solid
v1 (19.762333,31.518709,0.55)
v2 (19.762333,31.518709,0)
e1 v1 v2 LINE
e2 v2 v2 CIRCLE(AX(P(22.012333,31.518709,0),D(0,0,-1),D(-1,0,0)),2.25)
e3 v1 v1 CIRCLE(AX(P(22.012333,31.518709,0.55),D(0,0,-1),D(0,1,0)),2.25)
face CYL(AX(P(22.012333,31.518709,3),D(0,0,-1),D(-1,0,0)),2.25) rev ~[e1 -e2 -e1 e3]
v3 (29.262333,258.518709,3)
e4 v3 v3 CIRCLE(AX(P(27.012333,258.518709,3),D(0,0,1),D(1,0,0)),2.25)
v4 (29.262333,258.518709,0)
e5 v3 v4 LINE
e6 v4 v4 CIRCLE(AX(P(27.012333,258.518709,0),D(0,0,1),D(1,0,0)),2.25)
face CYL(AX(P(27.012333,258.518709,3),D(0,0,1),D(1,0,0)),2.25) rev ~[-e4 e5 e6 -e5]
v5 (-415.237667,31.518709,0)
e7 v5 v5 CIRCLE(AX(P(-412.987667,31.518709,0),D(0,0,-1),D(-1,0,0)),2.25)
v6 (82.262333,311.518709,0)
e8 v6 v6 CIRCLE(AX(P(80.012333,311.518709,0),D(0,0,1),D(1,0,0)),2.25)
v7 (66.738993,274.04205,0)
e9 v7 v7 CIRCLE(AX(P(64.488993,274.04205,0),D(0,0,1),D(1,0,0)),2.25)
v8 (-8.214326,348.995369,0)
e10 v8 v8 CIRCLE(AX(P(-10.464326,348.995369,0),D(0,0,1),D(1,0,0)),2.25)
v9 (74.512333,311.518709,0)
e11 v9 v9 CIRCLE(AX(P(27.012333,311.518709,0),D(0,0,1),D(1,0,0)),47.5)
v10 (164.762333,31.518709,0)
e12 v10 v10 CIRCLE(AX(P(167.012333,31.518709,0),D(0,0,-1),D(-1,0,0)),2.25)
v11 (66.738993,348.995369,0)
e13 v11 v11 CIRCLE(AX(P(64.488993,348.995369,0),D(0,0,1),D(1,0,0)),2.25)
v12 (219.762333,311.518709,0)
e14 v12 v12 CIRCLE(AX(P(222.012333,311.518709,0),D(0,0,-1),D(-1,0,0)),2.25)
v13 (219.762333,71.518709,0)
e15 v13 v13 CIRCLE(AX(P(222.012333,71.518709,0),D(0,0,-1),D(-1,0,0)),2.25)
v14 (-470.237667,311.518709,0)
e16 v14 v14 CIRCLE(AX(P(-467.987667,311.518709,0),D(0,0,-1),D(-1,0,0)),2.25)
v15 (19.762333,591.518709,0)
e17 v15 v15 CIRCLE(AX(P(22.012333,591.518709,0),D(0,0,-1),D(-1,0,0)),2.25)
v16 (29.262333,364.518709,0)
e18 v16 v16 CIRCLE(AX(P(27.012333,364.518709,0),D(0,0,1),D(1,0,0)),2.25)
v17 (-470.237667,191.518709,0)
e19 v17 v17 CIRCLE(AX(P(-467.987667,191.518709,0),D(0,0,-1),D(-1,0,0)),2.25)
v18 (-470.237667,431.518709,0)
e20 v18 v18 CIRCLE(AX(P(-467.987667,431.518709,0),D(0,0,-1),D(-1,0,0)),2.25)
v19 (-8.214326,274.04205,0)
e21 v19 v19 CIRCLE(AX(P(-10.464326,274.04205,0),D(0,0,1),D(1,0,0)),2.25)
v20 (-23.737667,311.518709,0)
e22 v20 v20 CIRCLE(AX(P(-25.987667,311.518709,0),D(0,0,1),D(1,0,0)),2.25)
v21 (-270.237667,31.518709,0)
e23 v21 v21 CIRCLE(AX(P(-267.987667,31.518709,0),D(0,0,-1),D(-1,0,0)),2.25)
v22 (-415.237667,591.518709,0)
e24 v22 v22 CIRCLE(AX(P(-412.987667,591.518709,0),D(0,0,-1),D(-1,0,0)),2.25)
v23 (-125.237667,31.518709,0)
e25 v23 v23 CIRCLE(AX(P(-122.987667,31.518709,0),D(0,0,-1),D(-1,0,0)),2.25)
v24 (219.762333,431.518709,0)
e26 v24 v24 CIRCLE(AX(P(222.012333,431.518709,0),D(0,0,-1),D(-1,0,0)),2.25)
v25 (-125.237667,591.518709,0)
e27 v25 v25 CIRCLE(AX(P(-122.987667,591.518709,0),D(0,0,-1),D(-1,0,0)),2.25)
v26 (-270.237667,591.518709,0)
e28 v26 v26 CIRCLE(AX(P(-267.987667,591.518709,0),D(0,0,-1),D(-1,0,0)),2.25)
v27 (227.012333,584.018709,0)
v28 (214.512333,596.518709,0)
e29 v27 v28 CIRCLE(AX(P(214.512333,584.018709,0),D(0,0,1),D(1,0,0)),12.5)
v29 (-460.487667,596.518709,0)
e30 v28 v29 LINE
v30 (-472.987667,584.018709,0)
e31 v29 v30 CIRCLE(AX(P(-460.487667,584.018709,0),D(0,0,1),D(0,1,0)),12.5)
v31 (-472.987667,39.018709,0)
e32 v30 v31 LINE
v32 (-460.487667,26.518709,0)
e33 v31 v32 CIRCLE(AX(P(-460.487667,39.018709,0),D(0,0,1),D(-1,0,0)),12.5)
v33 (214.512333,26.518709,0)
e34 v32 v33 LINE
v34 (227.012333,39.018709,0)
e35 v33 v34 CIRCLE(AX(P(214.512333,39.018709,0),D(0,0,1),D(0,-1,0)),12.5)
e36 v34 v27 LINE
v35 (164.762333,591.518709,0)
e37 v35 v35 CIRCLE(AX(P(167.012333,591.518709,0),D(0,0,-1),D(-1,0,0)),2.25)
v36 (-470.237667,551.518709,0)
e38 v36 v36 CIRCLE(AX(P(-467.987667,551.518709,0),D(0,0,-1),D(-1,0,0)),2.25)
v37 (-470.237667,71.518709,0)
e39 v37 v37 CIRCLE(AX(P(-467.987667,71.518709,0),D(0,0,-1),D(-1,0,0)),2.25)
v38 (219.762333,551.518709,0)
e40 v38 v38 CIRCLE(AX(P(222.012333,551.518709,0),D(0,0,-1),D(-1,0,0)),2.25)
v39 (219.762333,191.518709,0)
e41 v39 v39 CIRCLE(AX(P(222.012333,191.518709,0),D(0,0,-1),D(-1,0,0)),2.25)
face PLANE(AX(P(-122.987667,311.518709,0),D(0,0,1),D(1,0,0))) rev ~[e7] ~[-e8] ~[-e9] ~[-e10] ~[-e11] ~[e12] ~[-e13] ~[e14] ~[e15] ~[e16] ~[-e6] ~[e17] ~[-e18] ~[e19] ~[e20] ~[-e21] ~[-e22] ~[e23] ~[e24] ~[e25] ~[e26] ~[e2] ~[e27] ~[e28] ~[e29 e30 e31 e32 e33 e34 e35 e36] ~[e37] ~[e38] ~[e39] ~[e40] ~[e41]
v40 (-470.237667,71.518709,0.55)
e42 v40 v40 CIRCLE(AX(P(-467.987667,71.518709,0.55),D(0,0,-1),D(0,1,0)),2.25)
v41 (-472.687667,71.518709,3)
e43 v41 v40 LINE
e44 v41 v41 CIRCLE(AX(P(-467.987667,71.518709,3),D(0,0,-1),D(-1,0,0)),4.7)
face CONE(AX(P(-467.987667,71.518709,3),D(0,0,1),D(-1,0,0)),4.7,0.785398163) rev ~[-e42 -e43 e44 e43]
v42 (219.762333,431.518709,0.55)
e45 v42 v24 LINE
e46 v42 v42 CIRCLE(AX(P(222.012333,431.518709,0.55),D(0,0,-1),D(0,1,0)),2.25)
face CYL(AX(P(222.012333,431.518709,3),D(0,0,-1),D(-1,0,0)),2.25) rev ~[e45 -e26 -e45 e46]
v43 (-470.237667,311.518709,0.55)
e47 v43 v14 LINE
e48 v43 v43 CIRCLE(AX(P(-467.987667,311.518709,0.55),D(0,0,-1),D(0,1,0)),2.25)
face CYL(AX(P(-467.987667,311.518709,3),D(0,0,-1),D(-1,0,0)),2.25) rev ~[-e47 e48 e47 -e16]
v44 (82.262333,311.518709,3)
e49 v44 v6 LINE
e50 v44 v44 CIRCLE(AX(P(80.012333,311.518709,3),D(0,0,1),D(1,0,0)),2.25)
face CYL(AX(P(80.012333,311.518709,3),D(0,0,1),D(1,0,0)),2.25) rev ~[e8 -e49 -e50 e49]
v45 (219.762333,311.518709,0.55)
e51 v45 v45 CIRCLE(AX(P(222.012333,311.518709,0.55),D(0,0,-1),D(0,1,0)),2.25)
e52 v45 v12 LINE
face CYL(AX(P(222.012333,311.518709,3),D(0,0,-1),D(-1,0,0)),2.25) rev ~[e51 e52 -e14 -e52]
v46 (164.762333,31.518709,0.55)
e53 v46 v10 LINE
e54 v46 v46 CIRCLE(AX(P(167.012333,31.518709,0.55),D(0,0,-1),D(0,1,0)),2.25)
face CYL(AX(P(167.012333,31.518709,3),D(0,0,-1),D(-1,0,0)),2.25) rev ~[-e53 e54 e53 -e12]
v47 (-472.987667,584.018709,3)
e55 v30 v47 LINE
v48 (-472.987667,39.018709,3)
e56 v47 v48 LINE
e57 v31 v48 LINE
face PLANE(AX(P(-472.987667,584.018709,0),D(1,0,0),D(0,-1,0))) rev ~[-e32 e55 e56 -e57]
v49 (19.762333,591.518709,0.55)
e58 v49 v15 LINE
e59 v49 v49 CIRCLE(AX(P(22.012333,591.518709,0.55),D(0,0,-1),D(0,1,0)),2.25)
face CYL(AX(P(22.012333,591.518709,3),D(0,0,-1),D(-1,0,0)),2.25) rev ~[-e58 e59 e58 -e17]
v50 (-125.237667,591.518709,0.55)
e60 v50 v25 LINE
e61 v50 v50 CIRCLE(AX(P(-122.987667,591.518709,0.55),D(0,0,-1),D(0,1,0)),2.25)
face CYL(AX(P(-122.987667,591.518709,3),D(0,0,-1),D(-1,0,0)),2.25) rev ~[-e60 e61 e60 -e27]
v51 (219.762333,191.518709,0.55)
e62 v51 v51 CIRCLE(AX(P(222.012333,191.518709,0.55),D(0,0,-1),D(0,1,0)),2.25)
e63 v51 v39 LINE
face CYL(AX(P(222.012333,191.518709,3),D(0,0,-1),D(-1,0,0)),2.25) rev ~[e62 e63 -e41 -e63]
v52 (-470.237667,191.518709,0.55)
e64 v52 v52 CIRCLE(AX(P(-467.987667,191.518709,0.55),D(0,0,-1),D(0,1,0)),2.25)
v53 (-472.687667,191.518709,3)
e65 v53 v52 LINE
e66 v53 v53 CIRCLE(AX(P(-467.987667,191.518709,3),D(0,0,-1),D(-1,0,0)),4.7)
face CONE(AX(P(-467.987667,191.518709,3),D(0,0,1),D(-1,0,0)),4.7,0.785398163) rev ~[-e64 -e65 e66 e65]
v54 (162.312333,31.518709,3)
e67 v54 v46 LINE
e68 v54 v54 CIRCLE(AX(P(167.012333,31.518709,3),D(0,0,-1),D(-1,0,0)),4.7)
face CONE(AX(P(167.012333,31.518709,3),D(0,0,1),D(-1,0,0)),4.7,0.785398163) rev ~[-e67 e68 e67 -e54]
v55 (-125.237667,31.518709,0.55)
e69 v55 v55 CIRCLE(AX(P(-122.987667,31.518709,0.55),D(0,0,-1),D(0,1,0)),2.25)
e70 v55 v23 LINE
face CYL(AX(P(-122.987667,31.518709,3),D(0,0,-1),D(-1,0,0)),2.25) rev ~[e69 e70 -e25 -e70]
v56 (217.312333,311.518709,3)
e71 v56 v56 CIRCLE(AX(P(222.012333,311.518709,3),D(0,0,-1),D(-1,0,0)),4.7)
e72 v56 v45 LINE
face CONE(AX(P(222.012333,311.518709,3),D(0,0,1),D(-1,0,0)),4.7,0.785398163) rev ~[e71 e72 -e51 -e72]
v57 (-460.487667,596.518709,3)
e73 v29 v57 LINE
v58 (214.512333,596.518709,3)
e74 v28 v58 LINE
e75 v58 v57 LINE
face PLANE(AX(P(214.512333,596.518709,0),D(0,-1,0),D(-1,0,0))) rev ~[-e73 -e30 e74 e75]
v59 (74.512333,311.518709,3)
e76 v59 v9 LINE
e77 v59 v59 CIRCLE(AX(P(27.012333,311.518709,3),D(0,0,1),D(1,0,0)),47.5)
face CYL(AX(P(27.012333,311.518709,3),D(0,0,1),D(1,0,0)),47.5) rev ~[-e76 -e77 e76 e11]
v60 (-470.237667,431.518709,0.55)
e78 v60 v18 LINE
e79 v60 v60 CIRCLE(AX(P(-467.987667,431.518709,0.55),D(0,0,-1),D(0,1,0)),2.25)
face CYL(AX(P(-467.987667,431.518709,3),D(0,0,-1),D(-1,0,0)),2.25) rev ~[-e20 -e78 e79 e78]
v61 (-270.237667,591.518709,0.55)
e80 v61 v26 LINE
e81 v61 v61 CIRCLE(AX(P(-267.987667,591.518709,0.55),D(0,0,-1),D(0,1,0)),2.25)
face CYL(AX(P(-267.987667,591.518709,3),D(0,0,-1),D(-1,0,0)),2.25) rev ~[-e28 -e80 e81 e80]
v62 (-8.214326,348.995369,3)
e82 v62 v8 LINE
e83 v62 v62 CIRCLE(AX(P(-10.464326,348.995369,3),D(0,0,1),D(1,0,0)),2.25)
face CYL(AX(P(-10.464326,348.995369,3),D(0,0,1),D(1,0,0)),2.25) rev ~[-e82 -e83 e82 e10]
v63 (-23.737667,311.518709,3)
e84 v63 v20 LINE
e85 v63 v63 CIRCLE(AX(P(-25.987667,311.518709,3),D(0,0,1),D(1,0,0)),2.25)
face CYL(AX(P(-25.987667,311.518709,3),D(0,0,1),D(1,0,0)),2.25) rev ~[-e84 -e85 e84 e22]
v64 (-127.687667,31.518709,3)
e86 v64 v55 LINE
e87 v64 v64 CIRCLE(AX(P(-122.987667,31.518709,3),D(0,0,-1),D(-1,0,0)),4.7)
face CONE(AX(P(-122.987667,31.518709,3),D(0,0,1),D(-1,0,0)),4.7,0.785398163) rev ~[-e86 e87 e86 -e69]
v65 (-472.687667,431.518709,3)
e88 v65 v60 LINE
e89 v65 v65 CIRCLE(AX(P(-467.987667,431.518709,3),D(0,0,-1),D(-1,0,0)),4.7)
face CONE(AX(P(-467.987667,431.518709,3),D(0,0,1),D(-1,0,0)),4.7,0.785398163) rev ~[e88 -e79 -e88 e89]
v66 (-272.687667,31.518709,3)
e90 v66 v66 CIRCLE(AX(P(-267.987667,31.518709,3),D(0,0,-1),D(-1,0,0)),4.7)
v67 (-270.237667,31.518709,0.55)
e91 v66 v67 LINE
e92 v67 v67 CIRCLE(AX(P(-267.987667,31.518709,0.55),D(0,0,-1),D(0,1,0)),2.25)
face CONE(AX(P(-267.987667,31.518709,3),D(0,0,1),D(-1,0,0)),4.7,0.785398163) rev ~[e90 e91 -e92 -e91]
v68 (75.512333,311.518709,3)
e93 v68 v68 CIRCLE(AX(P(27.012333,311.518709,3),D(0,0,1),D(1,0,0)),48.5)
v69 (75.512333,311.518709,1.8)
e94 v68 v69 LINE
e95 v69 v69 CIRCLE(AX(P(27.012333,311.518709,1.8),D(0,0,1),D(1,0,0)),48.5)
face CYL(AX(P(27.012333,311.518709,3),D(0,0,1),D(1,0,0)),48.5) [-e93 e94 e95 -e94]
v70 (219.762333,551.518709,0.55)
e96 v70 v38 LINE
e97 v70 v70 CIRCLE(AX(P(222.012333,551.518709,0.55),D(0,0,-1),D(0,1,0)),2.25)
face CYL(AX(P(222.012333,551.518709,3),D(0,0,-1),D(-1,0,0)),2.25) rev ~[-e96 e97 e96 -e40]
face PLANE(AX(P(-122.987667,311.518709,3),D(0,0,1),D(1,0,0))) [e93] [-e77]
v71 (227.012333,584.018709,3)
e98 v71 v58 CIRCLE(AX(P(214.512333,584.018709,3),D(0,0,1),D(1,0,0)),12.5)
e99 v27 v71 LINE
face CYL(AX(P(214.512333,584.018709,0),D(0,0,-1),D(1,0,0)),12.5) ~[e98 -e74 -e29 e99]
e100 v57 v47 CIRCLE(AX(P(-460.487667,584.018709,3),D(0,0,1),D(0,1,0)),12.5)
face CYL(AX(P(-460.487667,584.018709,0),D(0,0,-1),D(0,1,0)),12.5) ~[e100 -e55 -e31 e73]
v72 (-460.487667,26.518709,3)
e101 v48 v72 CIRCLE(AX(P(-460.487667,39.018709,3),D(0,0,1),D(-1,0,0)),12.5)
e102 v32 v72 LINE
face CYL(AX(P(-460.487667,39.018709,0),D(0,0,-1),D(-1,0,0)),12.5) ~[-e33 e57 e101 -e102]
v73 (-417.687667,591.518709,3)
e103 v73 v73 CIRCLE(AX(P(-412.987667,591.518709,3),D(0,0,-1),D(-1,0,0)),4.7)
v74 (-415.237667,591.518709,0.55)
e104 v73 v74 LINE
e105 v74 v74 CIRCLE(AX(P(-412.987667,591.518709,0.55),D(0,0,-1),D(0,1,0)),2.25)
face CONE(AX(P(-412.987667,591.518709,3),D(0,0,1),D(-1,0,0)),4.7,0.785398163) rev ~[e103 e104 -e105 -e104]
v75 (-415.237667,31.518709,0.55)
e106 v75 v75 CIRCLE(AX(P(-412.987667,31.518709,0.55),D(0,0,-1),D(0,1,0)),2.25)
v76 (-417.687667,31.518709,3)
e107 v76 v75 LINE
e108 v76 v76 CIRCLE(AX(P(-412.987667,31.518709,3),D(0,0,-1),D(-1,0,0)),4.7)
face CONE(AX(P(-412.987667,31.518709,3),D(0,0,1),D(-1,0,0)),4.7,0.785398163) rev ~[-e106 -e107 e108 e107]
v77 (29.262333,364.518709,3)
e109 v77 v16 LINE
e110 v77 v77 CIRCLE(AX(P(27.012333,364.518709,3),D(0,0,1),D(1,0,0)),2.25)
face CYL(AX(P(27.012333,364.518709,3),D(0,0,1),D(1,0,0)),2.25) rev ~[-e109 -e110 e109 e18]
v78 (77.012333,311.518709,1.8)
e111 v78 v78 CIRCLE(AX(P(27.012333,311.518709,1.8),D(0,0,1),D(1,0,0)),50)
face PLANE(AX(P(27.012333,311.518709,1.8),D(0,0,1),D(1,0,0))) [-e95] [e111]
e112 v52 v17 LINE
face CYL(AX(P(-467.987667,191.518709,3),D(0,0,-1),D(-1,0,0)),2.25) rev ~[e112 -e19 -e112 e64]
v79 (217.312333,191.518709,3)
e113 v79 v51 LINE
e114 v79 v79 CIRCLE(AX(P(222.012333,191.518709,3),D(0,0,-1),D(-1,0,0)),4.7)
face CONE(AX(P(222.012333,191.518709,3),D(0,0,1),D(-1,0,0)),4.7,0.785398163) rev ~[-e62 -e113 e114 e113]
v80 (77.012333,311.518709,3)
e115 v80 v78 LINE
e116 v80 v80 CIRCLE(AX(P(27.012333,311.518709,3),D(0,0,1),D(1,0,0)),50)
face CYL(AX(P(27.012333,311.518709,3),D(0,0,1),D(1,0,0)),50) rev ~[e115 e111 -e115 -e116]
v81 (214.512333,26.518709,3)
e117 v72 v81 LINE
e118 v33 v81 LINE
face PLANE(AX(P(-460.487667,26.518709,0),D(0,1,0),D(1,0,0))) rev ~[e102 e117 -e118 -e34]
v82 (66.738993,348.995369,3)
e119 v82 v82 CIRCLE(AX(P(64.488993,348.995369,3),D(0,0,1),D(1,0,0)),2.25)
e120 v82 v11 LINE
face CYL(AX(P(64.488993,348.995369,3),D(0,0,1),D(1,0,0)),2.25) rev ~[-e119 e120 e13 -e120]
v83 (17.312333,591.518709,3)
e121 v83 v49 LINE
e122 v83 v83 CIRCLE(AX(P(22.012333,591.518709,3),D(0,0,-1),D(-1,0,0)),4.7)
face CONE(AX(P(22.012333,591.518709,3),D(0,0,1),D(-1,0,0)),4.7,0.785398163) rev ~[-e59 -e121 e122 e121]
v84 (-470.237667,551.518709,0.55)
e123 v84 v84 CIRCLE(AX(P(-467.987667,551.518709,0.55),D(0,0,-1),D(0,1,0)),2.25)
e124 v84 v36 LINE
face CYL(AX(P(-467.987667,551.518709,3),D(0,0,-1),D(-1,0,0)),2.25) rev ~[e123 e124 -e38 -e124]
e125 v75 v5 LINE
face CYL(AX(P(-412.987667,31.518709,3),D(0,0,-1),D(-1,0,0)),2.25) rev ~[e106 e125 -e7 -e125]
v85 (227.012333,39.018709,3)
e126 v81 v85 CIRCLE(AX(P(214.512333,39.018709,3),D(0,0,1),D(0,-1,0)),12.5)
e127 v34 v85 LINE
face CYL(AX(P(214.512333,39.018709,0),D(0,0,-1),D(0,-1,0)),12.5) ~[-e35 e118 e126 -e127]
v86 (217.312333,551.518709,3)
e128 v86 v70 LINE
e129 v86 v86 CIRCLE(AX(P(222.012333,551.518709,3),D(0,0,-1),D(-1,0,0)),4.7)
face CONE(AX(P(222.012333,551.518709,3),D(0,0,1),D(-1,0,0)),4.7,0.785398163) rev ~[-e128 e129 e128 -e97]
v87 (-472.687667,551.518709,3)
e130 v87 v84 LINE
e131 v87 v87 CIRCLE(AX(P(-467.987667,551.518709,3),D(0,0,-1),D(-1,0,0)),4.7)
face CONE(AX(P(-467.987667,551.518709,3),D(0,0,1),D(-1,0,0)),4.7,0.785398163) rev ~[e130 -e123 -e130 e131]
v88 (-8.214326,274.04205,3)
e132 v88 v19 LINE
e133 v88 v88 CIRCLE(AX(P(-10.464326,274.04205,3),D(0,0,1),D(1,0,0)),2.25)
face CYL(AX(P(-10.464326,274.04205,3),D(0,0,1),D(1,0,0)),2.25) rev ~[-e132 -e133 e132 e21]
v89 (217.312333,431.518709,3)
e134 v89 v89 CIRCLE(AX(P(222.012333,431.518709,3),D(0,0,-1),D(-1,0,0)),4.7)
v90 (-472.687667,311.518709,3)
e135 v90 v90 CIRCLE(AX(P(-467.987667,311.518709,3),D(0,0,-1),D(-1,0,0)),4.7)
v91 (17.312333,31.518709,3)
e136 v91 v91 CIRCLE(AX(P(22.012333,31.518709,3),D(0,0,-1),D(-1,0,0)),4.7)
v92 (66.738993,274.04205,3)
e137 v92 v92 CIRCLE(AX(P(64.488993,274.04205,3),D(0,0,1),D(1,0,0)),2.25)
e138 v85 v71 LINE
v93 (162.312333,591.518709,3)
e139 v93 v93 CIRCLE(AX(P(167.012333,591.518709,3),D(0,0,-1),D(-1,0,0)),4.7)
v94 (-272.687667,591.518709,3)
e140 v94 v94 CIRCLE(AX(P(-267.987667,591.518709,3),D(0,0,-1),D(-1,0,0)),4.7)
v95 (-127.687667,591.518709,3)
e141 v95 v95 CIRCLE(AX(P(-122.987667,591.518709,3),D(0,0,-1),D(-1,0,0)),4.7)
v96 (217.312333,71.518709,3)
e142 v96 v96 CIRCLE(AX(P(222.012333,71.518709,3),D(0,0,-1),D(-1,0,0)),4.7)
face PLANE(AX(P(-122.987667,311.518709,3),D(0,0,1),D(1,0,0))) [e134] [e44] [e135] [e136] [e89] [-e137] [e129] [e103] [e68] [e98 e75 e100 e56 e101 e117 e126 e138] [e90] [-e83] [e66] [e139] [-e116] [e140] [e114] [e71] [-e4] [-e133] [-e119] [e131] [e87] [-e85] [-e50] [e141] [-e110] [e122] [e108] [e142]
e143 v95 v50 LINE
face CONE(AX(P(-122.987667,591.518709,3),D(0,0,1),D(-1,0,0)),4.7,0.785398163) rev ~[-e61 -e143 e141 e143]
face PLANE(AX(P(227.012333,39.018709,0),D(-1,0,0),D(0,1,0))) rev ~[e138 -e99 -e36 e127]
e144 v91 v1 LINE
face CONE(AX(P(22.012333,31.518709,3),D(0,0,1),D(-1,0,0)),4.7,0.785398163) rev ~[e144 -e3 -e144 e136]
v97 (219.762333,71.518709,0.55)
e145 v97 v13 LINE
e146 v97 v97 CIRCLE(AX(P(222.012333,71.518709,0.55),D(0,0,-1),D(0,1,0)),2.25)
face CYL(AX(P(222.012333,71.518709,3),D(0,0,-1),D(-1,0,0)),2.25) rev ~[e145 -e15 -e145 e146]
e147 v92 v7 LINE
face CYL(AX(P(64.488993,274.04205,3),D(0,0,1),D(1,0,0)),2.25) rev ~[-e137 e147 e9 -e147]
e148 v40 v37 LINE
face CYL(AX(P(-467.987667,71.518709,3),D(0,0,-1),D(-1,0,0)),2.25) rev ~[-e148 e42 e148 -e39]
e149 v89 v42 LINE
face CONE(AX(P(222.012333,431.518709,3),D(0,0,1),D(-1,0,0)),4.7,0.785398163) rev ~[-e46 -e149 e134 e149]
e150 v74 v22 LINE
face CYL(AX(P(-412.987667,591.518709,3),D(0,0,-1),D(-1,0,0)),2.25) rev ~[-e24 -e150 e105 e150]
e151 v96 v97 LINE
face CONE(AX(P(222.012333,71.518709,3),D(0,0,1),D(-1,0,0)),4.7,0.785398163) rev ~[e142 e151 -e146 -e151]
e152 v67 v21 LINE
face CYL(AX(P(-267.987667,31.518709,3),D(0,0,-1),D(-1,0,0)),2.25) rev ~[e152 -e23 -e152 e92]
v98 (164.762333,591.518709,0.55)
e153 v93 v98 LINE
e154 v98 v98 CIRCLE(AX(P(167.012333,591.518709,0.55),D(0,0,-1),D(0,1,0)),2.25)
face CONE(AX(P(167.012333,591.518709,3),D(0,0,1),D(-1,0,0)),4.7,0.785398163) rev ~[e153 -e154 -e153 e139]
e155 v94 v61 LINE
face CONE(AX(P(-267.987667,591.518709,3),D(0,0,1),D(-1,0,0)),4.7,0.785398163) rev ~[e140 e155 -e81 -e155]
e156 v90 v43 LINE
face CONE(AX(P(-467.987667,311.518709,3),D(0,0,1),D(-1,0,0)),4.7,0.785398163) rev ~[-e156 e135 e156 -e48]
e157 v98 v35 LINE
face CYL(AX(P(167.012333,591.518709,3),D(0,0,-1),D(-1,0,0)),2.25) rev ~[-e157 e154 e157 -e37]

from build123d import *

# Parameters (mm, degrees)
EXTRUDE_1_DEPTH              = 3
HOLE_WIZARD_M4_1_D           = 4.5
HOLE_WIZARD_M4_1_DEPTH       = 10.1
HOLE_WIZARD_M4_1_CSINK_D     = 9.4
HOLE_WIZARD_M4_1_CSINK_ANGLE = 90
HOLE_WIZARD_M4_1_TIP         = 1.351936393
SKETCH_4_R                   = 47.5
CUT_EXTRUDE_1_DEPTH          = 12
SKETCH_5_R                   = 50
SKETCH_5_R_2                 = 48.5
CUT_EXTRUDE_2_DEPTH          = 1.2
SKETCH_6_R                   = 2.25
CUT_EXTRUDE_3_DEPTH          = 10


with BuildPart() as part:
    # 草图1 → 凸台-拉伸1 (new body)
    with BuildSketch(Plane.XY):
        with BuildLine():
            Line((227.012333385, 39.0187092), (227.012333385, 584.0187092))
            ThreePointArc((227.012333385, 584.0187092), (223.35116815, 592.857543965), (214.512333385, 596.5187092))
            Line((214.512333385, 596.5187092), (-460.487666615, 596.5187092))
            ThreePointArc((-460.487666615, 596.5187092), (-469.326501379, 592.857543965), (-472.987666615, 584.0187092))
            Line((-472.987666615, 584.0187092), (-472.987666615, 39.0187092))
            ThreePointArc((-472.987666615, 39.0187092), (-469.326501379, 30.179874435), (-460.487666615, 26.5187092))
            Line((-460.487666615, 26.5187092), (214.512333385, 26.5187092))
            ThreePointArc((214.512333385, 26.5187092), (223.35116815, 30.179874435), (227.012333385, 39.0187092))
        make_face()
    extrude(amount=EXTRUDE_1_DEPTH)

    # M4 锥坑平头螺钉的锥形沉头孔1
    with Locations(Plane.XY.offset(3)):
        with Locations((222.012333385, 71.5187092), (222.012333385, 191.5187092), (222.012333385, 311.5187092), (222.012333385, 431.5187092), (222.012333385, 551.5187092), (167.012333385, 591.5187092), (22.012333385, 591.5187092), (-122.987666615, 591.5187092), (-267.987666615, 591.5187092), (-412.987666615, 591.5187092), (-467.987666615, 551.5187092), (-467.987666615, 431.5187092), (-467.987666615, 311.5187092), (-467.987666615, 191.5187092), (-467.987666615, 71.5187092), (-412.987666615, 31.5187092), (-267.987666615, 31.5187092), (-122.987666615, 31.5187092), (22.012333385, 31.5187092), (167.012333385, 31.5187092)):
            CounterSinkHole(HOLE_WIZARD_M4_1_D / 2, HOLE_WIZARD_M4_1_CSINK_D / 2, depth=HOLE_WIZARD_M4_1_DEPTH, counter_sink_angle=HOLE_WIZARD_M4_1_CSINK_ANGLE)
            with Locations((0, 0, -(HOLE_WIZARD_M4_1_DEPTH + HOLE_WIZARD_M4_1_TIP / 2))):  # 118° drill point
                Cone(0, HOLE_WIZARD_M4_1_D / 2, HOLE_WIZARD_M4_1_TIP, mode=Mode.SUBTRACT)

    # 草图4 → 切除-拉伸1 (cut)
    with BuildSketch(Plane.XY.offset(3)):
        with Locations((27.012333385, 311.5187092)):
            Circle(SKETCH_4_R)
    extrude(amount=-CUT_EXTRUDE_1_DEPTH, mode=Mode.SUBTRACT)

    # 草图5 → 切除-拉伸2 (cut)
    with BuildSketch(Plane.XY.offset(3)):
        with Locations((27.012333385, 311.5187092)):
            Circle(SKETCH_5_R)
        with Locations((27.012333385, 311.5187092)):
            Circle(SKETCH_5_R_2, mode=Mode.SUBTRACT)
    extrude(amount=-CUT_EXTRUDE_2_DEPTH, mode=Mode.SUBTRACT)

    # 草图6 → 切除-拉伸3 (cut)
    with BuildSketch(Plane.XY.offset(3)):
        with Locations((27.012333385, 258.5187092)):
            Circle(SKETCH_6_R)
        with Locations((-10.464326017, 274.042049797)):
            Circle(SKETCH_6_R)
        with Locations((-25.987666615, 311.5187092)):
            Circle(SKETCH_6_R)
        with Locations((-10.464326017, 348.995368603)):
            Circle(SKETCH_6_R)
        with Locations((27.012333385, 364.5187092)):
            Circle(SKETCH_6_R)
        with Locations((64.488992788, 348.995368603)):
            Circle(SKETCH_6_R)
        with Locations((80.012333385, 311.5187092)):
            Circle(SKETCH_6_R)
        with Locations((64.488992788, 274.042049797)):
            Circle(SKETCH_6_R)
    extrude(amount=-CUT_EXTRUDE_3_DEPTH, mode=Mode.SUBTRACT)


solid = part.part
